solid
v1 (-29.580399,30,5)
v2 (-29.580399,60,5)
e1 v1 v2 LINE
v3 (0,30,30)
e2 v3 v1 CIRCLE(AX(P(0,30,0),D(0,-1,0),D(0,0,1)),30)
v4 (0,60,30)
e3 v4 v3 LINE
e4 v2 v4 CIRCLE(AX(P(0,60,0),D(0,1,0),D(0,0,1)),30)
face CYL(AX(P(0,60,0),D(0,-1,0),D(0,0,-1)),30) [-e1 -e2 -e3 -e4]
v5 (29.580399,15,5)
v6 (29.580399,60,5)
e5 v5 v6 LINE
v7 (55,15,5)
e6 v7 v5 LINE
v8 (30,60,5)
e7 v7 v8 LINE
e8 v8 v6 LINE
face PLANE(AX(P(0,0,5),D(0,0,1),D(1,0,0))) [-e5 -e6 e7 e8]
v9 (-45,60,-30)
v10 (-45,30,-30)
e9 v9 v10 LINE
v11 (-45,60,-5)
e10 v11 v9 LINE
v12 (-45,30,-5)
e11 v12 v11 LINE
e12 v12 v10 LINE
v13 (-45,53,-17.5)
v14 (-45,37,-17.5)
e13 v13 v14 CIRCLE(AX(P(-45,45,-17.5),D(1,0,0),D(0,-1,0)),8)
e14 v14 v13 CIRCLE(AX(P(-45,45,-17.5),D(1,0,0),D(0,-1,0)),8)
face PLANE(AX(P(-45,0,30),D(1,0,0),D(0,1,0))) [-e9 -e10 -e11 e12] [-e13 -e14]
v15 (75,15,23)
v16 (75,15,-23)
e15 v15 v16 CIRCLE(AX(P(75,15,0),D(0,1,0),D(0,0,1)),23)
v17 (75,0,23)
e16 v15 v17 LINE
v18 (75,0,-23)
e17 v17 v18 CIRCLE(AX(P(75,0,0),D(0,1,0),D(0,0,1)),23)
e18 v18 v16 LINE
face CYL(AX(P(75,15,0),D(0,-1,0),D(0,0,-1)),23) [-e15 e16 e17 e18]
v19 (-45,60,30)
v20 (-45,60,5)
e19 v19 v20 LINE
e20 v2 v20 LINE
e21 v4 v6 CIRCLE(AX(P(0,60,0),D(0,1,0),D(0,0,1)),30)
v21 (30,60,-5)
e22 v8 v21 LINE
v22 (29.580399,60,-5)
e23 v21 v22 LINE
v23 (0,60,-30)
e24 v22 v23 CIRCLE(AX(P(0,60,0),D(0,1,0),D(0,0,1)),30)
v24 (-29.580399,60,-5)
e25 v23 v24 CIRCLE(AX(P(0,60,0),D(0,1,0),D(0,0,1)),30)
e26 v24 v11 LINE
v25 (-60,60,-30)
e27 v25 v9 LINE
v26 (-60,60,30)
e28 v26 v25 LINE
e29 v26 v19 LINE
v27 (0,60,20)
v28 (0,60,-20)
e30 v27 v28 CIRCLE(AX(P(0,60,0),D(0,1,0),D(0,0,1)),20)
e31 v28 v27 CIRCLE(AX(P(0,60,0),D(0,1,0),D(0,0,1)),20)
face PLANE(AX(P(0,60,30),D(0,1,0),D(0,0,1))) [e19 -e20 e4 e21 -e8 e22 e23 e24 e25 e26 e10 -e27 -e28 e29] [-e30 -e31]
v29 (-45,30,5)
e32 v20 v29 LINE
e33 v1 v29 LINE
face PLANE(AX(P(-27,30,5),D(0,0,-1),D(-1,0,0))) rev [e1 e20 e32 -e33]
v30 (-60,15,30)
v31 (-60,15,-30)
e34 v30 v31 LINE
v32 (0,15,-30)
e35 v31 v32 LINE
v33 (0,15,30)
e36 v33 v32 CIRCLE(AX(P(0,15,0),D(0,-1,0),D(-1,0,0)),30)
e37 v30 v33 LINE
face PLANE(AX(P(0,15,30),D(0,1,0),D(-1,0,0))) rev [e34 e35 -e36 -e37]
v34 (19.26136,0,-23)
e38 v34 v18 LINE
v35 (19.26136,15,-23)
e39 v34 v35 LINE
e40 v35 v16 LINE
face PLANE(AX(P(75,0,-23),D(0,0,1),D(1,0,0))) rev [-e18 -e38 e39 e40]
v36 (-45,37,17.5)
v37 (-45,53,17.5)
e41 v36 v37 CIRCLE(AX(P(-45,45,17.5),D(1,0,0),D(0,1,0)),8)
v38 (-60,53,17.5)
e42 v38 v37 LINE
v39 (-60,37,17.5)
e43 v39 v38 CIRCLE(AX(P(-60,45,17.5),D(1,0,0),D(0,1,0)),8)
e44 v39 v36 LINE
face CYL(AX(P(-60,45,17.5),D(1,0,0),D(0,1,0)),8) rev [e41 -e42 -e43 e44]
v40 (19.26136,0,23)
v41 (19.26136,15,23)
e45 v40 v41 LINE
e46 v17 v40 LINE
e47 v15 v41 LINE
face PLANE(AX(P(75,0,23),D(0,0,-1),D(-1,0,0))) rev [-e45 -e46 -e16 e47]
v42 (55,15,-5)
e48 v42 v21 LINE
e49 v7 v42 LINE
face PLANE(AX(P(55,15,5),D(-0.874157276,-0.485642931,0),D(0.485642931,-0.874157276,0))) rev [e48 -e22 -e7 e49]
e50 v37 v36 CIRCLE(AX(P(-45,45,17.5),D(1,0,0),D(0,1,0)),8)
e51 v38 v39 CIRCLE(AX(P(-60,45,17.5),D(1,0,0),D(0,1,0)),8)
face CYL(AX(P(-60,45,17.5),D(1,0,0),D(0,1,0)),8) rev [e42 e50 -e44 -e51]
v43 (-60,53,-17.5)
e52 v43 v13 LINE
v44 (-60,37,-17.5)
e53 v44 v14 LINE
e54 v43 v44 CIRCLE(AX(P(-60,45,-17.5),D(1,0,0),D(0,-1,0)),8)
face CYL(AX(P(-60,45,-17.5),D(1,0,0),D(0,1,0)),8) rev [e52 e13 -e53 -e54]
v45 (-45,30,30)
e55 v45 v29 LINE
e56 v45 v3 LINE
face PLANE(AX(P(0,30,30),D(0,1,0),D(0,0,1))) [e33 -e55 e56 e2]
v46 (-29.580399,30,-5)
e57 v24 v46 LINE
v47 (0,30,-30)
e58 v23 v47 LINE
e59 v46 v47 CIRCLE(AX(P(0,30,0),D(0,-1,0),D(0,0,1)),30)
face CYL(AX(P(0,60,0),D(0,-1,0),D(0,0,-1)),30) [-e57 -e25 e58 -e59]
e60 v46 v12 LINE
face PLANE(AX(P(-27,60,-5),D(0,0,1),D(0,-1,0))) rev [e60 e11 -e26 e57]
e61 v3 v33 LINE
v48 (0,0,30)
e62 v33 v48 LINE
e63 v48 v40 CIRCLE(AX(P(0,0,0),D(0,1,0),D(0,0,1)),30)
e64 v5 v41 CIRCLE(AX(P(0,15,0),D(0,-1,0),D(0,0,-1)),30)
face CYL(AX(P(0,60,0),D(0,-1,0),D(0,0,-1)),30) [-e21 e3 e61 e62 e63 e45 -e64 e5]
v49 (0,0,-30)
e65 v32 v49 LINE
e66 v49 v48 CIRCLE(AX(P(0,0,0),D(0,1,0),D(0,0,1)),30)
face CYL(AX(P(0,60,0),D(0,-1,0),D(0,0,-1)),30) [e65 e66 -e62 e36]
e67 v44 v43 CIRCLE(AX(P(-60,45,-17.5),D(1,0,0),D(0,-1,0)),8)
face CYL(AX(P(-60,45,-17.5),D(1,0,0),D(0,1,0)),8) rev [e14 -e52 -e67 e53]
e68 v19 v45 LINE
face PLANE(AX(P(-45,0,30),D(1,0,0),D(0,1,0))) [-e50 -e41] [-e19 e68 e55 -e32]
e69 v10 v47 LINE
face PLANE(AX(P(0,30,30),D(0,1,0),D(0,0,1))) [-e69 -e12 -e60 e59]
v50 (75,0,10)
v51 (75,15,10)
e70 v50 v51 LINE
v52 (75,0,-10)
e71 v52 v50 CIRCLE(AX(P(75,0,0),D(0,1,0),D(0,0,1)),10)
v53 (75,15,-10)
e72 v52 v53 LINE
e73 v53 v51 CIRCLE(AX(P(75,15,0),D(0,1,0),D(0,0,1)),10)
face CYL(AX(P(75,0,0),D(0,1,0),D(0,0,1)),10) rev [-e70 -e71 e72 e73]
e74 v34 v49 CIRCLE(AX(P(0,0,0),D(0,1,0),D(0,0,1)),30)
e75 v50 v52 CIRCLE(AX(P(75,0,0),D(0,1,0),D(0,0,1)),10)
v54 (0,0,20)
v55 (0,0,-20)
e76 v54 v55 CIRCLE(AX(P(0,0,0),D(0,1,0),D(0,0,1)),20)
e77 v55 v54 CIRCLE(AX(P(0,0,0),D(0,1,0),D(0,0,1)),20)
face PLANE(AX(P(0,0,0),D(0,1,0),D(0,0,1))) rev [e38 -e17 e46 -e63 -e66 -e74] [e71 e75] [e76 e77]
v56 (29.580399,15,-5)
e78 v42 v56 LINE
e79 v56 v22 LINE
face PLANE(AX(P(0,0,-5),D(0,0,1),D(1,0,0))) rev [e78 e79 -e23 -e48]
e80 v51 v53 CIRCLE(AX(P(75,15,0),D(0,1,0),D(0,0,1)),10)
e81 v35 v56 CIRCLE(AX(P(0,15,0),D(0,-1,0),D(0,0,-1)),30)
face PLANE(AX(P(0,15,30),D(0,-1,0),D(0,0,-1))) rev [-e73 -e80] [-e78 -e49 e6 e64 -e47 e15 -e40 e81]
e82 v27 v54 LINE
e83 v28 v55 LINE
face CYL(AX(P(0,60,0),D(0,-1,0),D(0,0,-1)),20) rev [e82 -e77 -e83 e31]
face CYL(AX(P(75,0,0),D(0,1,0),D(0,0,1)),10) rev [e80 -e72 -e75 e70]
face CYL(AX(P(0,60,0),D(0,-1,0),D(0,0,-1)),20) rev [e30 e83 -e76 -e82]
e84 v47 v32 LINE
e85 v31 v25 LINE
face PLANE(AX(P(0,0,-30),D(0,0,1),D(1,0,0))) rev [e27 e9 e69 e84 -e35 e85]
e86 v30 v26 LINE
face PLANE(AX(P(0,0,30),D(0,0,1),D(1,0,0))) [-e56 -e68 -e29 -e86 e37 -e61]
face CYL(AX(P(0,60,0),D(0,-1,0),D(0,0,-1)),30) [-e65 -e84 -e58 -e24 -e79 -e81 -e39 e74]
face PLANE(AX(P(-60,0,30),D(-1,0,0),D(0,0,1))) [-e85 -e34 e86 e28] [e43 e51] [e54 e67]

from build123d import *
from build123d.topology import SkipClean

# Parameters (mm, degrees)
BRACKET_BODY_DEPTH      = 30
BRACKET_BODY_SKETCH_W   = 75
BRACKET_BODY_SKETCH_H   = 15
BRACKET_BODY_2_DEPTH    = 30
COLUMN_BORE_SKETCH_R    = 20
COLUMN_BORE_40_DEPTH    = 60
COLUMN_BOSS_SKETCH_R    = 30
COLUMN_BOSS_SKETCH_R_2  = 20
COLUMN_BOSS_60_DEPTH    = 60
BASE_COLLAR_SKETCH_R    = 23
BASE_COLLAR_46_DEPTH    = 15
BODY_TRIM_CUT_SKETCH_R  = 10
BODY_TRIM_CUT_DEPTH     = 112.933015683
SIDE_BLOCK_CUT_SKETCH_R = 8
SIDE_BLOCK_CUT_DEPTH    = 158.952524513
PAD_BOSS_18MM_DEPTH     = 18
SUPPORT_RIB_DEPTH       = 5


with BuildPart() as part:
    # Bracket Body Sketch → Bracket Body (new, symmetric)
    with BuildSketch(Plane.XY):
        Polygon((-60, 15), (-60, 60), (-45, 60), (-45, 30), (0, 30), (0, 15), align=None)
    extrude(amount=BRACKET_BODY_DEPTH, both=True)


with BuildPart() as body_2:
    # Bracket Body Sketch → Bracket Body 2 (new, symmetric)
    with BuildSketch(Plane.XY):
        with Locations((37.5, 7.5)):
            Rectangle(BRACKET_BODY_SKETCH_W, BRACKET_BODY_SKETCH_H)
    extrude(amount=BRACKET_BODY_2_DEPTH, both=True)


with BuildPart() as column_bore_40_tool:
    # Column Bore Sketch → Column Bore Ø40 (new body)
    with BuildSketch(Plane(origin=(0, 0, 0), x_dir=(1, 0, 0), z_dir=(0, 1, 0))):
        Circle(COLUMN_BORE_SKETCH_R)
    extrude(amount=COLUMN_BORE_40_DEPTH)


with BuildPart() as part_1:
    add(part.part)

    # Column Bore Ø40: cut by column_bore_40_tool
    add(column_bore_40_tool.part, mode=Mode.SUBTRACT)



with BuildPart() as body_2_1:
    add(body_2.part)

    # Column Bore Ø40: cut by column_bore_40_tool
    add(column_bore_40_tool.part, mode=Mode.SUBTRACT)


with BuildPart() as part_2:
    add(part_1.part)

    add(body_2_1.part)  # Column Boss Ø60 merges body 2
    # Column Boss Sketch → Column Boss Ø60 (add)
    with BuildSketch(Plane(origin=(0, 0, 0), x_dir=(1, 0, 0), z_dir=(0, 1, 0))):
        with Locations(Location((0, 0, 0), (0, 0, 270))):
            Circle(COLUMN_BOSS_SKETCH_R)
        with Locations(Location((0, 0, 0), (0, 0, 270))):
            Circle(COLUMN_BOSS_SKETCH_R_2, mode=Mode.SUBTRACT)
    extrude(amount=COLUMN_BOSS_60_DEPTH)

    # Base Collar Sketch → Base Collar Ø46 (add)
    with BuildSketch(Plane(origin=(0, 0, 0), x_dir=(1, 0, 0), z_dir=(0, 1, 0))):
        with Locations((75, 0)):
            Circle(BASE_COLLAR_SKETCH_R)
    extrude(amount=BASE_COLLAR_46_DEPTH)

    # Body Trim Cut Sketch → Body Trim Cut (cut, through all)
    with SkipClean():  # the faces are left unmerged after this step: merging them gives an invalid solid
        with BuildSketch(Plane(origin=(0, 15, 0), x_dir=(1, 0, 0), z_dir=(0, 1, 0))):
            with Locations(Location((75, 0, 0), (0, 0, 270))):
                Circle(BODY_TRIM_CUT_SKETCH_R)
            with BuildLine():
                Line((75, 23), (19.261360284, 23))
                ThreePointArc((19.261360284, 23), (10.246950766, 28.19574436), (0, 30))
                Line((0, 30), (75, 30))
                Line((75, 30), (75, 23))
            make_face()
            with BuildLine():
                Line((75, -23), (75, -30))
                Line((75, -30), (0, -30))
                ThreePointArc((0, -30), (10.246950766, -28.19574436), (19.261360284, -23))
                Line((19.261360284, -23), (75, -23))
            make_face()
        extrude(amount=-BODY_TRIM_CUT_DEPTH, mode=Mode.SUBTRACT)

    # Side Block Cut Sketch → Side Block Cut (cut, through all)
    with SkipClean():  # the faces are left unmerged after this step: merging them gives an invalid solid
        with BuildSketch(Plane(origin=(-45, 0, 0), x_dir=(0, 0, -1), z_dir=(1, 0, 0))):
            with Locations(Location((-17.5, 45, 0), (0, 0, 90))):
                Circle(SIDE_BLOCK_CUT_SKETCH_R)
            with Locations(Location((17.5, 45, 0), (0, 0, 270))):
                Circle(SIDE_BLOCK_CUT_SKETCH_R)
        extrude(amount=-SIDE_BLOCK_CUT_DEPTH, mode=Mode.SUBTRACT)

    # Pad Boss Sketch → Pad Boss 18mm (add)
    with SkipClean():  # the faces are left unmerged after this step: merging them gives an invalid solid
        with BuildSketch(Plane(origin=(-45, 0, 0), x_dir=(0, 0, -1), z_dir=(1, 0, 0))):
            Polygon((0, 60), (5, 60), (5, 30), (-5, 30), (-5, 60), align=None)
        extrude(amount=PAD_BOSS_18MM_DEPTH)

    # Support Rib Sketch → Support Rib (add, symmetric)
    with BuildSketch(Plane.XY):
        Polygon((30, 15), (55, 15), (30, 60), (20, 60), (20, 15), align=None)
    extrude(amount=SUPPORT_RIB_DEPTH, both=True)


solid = part_2.part
